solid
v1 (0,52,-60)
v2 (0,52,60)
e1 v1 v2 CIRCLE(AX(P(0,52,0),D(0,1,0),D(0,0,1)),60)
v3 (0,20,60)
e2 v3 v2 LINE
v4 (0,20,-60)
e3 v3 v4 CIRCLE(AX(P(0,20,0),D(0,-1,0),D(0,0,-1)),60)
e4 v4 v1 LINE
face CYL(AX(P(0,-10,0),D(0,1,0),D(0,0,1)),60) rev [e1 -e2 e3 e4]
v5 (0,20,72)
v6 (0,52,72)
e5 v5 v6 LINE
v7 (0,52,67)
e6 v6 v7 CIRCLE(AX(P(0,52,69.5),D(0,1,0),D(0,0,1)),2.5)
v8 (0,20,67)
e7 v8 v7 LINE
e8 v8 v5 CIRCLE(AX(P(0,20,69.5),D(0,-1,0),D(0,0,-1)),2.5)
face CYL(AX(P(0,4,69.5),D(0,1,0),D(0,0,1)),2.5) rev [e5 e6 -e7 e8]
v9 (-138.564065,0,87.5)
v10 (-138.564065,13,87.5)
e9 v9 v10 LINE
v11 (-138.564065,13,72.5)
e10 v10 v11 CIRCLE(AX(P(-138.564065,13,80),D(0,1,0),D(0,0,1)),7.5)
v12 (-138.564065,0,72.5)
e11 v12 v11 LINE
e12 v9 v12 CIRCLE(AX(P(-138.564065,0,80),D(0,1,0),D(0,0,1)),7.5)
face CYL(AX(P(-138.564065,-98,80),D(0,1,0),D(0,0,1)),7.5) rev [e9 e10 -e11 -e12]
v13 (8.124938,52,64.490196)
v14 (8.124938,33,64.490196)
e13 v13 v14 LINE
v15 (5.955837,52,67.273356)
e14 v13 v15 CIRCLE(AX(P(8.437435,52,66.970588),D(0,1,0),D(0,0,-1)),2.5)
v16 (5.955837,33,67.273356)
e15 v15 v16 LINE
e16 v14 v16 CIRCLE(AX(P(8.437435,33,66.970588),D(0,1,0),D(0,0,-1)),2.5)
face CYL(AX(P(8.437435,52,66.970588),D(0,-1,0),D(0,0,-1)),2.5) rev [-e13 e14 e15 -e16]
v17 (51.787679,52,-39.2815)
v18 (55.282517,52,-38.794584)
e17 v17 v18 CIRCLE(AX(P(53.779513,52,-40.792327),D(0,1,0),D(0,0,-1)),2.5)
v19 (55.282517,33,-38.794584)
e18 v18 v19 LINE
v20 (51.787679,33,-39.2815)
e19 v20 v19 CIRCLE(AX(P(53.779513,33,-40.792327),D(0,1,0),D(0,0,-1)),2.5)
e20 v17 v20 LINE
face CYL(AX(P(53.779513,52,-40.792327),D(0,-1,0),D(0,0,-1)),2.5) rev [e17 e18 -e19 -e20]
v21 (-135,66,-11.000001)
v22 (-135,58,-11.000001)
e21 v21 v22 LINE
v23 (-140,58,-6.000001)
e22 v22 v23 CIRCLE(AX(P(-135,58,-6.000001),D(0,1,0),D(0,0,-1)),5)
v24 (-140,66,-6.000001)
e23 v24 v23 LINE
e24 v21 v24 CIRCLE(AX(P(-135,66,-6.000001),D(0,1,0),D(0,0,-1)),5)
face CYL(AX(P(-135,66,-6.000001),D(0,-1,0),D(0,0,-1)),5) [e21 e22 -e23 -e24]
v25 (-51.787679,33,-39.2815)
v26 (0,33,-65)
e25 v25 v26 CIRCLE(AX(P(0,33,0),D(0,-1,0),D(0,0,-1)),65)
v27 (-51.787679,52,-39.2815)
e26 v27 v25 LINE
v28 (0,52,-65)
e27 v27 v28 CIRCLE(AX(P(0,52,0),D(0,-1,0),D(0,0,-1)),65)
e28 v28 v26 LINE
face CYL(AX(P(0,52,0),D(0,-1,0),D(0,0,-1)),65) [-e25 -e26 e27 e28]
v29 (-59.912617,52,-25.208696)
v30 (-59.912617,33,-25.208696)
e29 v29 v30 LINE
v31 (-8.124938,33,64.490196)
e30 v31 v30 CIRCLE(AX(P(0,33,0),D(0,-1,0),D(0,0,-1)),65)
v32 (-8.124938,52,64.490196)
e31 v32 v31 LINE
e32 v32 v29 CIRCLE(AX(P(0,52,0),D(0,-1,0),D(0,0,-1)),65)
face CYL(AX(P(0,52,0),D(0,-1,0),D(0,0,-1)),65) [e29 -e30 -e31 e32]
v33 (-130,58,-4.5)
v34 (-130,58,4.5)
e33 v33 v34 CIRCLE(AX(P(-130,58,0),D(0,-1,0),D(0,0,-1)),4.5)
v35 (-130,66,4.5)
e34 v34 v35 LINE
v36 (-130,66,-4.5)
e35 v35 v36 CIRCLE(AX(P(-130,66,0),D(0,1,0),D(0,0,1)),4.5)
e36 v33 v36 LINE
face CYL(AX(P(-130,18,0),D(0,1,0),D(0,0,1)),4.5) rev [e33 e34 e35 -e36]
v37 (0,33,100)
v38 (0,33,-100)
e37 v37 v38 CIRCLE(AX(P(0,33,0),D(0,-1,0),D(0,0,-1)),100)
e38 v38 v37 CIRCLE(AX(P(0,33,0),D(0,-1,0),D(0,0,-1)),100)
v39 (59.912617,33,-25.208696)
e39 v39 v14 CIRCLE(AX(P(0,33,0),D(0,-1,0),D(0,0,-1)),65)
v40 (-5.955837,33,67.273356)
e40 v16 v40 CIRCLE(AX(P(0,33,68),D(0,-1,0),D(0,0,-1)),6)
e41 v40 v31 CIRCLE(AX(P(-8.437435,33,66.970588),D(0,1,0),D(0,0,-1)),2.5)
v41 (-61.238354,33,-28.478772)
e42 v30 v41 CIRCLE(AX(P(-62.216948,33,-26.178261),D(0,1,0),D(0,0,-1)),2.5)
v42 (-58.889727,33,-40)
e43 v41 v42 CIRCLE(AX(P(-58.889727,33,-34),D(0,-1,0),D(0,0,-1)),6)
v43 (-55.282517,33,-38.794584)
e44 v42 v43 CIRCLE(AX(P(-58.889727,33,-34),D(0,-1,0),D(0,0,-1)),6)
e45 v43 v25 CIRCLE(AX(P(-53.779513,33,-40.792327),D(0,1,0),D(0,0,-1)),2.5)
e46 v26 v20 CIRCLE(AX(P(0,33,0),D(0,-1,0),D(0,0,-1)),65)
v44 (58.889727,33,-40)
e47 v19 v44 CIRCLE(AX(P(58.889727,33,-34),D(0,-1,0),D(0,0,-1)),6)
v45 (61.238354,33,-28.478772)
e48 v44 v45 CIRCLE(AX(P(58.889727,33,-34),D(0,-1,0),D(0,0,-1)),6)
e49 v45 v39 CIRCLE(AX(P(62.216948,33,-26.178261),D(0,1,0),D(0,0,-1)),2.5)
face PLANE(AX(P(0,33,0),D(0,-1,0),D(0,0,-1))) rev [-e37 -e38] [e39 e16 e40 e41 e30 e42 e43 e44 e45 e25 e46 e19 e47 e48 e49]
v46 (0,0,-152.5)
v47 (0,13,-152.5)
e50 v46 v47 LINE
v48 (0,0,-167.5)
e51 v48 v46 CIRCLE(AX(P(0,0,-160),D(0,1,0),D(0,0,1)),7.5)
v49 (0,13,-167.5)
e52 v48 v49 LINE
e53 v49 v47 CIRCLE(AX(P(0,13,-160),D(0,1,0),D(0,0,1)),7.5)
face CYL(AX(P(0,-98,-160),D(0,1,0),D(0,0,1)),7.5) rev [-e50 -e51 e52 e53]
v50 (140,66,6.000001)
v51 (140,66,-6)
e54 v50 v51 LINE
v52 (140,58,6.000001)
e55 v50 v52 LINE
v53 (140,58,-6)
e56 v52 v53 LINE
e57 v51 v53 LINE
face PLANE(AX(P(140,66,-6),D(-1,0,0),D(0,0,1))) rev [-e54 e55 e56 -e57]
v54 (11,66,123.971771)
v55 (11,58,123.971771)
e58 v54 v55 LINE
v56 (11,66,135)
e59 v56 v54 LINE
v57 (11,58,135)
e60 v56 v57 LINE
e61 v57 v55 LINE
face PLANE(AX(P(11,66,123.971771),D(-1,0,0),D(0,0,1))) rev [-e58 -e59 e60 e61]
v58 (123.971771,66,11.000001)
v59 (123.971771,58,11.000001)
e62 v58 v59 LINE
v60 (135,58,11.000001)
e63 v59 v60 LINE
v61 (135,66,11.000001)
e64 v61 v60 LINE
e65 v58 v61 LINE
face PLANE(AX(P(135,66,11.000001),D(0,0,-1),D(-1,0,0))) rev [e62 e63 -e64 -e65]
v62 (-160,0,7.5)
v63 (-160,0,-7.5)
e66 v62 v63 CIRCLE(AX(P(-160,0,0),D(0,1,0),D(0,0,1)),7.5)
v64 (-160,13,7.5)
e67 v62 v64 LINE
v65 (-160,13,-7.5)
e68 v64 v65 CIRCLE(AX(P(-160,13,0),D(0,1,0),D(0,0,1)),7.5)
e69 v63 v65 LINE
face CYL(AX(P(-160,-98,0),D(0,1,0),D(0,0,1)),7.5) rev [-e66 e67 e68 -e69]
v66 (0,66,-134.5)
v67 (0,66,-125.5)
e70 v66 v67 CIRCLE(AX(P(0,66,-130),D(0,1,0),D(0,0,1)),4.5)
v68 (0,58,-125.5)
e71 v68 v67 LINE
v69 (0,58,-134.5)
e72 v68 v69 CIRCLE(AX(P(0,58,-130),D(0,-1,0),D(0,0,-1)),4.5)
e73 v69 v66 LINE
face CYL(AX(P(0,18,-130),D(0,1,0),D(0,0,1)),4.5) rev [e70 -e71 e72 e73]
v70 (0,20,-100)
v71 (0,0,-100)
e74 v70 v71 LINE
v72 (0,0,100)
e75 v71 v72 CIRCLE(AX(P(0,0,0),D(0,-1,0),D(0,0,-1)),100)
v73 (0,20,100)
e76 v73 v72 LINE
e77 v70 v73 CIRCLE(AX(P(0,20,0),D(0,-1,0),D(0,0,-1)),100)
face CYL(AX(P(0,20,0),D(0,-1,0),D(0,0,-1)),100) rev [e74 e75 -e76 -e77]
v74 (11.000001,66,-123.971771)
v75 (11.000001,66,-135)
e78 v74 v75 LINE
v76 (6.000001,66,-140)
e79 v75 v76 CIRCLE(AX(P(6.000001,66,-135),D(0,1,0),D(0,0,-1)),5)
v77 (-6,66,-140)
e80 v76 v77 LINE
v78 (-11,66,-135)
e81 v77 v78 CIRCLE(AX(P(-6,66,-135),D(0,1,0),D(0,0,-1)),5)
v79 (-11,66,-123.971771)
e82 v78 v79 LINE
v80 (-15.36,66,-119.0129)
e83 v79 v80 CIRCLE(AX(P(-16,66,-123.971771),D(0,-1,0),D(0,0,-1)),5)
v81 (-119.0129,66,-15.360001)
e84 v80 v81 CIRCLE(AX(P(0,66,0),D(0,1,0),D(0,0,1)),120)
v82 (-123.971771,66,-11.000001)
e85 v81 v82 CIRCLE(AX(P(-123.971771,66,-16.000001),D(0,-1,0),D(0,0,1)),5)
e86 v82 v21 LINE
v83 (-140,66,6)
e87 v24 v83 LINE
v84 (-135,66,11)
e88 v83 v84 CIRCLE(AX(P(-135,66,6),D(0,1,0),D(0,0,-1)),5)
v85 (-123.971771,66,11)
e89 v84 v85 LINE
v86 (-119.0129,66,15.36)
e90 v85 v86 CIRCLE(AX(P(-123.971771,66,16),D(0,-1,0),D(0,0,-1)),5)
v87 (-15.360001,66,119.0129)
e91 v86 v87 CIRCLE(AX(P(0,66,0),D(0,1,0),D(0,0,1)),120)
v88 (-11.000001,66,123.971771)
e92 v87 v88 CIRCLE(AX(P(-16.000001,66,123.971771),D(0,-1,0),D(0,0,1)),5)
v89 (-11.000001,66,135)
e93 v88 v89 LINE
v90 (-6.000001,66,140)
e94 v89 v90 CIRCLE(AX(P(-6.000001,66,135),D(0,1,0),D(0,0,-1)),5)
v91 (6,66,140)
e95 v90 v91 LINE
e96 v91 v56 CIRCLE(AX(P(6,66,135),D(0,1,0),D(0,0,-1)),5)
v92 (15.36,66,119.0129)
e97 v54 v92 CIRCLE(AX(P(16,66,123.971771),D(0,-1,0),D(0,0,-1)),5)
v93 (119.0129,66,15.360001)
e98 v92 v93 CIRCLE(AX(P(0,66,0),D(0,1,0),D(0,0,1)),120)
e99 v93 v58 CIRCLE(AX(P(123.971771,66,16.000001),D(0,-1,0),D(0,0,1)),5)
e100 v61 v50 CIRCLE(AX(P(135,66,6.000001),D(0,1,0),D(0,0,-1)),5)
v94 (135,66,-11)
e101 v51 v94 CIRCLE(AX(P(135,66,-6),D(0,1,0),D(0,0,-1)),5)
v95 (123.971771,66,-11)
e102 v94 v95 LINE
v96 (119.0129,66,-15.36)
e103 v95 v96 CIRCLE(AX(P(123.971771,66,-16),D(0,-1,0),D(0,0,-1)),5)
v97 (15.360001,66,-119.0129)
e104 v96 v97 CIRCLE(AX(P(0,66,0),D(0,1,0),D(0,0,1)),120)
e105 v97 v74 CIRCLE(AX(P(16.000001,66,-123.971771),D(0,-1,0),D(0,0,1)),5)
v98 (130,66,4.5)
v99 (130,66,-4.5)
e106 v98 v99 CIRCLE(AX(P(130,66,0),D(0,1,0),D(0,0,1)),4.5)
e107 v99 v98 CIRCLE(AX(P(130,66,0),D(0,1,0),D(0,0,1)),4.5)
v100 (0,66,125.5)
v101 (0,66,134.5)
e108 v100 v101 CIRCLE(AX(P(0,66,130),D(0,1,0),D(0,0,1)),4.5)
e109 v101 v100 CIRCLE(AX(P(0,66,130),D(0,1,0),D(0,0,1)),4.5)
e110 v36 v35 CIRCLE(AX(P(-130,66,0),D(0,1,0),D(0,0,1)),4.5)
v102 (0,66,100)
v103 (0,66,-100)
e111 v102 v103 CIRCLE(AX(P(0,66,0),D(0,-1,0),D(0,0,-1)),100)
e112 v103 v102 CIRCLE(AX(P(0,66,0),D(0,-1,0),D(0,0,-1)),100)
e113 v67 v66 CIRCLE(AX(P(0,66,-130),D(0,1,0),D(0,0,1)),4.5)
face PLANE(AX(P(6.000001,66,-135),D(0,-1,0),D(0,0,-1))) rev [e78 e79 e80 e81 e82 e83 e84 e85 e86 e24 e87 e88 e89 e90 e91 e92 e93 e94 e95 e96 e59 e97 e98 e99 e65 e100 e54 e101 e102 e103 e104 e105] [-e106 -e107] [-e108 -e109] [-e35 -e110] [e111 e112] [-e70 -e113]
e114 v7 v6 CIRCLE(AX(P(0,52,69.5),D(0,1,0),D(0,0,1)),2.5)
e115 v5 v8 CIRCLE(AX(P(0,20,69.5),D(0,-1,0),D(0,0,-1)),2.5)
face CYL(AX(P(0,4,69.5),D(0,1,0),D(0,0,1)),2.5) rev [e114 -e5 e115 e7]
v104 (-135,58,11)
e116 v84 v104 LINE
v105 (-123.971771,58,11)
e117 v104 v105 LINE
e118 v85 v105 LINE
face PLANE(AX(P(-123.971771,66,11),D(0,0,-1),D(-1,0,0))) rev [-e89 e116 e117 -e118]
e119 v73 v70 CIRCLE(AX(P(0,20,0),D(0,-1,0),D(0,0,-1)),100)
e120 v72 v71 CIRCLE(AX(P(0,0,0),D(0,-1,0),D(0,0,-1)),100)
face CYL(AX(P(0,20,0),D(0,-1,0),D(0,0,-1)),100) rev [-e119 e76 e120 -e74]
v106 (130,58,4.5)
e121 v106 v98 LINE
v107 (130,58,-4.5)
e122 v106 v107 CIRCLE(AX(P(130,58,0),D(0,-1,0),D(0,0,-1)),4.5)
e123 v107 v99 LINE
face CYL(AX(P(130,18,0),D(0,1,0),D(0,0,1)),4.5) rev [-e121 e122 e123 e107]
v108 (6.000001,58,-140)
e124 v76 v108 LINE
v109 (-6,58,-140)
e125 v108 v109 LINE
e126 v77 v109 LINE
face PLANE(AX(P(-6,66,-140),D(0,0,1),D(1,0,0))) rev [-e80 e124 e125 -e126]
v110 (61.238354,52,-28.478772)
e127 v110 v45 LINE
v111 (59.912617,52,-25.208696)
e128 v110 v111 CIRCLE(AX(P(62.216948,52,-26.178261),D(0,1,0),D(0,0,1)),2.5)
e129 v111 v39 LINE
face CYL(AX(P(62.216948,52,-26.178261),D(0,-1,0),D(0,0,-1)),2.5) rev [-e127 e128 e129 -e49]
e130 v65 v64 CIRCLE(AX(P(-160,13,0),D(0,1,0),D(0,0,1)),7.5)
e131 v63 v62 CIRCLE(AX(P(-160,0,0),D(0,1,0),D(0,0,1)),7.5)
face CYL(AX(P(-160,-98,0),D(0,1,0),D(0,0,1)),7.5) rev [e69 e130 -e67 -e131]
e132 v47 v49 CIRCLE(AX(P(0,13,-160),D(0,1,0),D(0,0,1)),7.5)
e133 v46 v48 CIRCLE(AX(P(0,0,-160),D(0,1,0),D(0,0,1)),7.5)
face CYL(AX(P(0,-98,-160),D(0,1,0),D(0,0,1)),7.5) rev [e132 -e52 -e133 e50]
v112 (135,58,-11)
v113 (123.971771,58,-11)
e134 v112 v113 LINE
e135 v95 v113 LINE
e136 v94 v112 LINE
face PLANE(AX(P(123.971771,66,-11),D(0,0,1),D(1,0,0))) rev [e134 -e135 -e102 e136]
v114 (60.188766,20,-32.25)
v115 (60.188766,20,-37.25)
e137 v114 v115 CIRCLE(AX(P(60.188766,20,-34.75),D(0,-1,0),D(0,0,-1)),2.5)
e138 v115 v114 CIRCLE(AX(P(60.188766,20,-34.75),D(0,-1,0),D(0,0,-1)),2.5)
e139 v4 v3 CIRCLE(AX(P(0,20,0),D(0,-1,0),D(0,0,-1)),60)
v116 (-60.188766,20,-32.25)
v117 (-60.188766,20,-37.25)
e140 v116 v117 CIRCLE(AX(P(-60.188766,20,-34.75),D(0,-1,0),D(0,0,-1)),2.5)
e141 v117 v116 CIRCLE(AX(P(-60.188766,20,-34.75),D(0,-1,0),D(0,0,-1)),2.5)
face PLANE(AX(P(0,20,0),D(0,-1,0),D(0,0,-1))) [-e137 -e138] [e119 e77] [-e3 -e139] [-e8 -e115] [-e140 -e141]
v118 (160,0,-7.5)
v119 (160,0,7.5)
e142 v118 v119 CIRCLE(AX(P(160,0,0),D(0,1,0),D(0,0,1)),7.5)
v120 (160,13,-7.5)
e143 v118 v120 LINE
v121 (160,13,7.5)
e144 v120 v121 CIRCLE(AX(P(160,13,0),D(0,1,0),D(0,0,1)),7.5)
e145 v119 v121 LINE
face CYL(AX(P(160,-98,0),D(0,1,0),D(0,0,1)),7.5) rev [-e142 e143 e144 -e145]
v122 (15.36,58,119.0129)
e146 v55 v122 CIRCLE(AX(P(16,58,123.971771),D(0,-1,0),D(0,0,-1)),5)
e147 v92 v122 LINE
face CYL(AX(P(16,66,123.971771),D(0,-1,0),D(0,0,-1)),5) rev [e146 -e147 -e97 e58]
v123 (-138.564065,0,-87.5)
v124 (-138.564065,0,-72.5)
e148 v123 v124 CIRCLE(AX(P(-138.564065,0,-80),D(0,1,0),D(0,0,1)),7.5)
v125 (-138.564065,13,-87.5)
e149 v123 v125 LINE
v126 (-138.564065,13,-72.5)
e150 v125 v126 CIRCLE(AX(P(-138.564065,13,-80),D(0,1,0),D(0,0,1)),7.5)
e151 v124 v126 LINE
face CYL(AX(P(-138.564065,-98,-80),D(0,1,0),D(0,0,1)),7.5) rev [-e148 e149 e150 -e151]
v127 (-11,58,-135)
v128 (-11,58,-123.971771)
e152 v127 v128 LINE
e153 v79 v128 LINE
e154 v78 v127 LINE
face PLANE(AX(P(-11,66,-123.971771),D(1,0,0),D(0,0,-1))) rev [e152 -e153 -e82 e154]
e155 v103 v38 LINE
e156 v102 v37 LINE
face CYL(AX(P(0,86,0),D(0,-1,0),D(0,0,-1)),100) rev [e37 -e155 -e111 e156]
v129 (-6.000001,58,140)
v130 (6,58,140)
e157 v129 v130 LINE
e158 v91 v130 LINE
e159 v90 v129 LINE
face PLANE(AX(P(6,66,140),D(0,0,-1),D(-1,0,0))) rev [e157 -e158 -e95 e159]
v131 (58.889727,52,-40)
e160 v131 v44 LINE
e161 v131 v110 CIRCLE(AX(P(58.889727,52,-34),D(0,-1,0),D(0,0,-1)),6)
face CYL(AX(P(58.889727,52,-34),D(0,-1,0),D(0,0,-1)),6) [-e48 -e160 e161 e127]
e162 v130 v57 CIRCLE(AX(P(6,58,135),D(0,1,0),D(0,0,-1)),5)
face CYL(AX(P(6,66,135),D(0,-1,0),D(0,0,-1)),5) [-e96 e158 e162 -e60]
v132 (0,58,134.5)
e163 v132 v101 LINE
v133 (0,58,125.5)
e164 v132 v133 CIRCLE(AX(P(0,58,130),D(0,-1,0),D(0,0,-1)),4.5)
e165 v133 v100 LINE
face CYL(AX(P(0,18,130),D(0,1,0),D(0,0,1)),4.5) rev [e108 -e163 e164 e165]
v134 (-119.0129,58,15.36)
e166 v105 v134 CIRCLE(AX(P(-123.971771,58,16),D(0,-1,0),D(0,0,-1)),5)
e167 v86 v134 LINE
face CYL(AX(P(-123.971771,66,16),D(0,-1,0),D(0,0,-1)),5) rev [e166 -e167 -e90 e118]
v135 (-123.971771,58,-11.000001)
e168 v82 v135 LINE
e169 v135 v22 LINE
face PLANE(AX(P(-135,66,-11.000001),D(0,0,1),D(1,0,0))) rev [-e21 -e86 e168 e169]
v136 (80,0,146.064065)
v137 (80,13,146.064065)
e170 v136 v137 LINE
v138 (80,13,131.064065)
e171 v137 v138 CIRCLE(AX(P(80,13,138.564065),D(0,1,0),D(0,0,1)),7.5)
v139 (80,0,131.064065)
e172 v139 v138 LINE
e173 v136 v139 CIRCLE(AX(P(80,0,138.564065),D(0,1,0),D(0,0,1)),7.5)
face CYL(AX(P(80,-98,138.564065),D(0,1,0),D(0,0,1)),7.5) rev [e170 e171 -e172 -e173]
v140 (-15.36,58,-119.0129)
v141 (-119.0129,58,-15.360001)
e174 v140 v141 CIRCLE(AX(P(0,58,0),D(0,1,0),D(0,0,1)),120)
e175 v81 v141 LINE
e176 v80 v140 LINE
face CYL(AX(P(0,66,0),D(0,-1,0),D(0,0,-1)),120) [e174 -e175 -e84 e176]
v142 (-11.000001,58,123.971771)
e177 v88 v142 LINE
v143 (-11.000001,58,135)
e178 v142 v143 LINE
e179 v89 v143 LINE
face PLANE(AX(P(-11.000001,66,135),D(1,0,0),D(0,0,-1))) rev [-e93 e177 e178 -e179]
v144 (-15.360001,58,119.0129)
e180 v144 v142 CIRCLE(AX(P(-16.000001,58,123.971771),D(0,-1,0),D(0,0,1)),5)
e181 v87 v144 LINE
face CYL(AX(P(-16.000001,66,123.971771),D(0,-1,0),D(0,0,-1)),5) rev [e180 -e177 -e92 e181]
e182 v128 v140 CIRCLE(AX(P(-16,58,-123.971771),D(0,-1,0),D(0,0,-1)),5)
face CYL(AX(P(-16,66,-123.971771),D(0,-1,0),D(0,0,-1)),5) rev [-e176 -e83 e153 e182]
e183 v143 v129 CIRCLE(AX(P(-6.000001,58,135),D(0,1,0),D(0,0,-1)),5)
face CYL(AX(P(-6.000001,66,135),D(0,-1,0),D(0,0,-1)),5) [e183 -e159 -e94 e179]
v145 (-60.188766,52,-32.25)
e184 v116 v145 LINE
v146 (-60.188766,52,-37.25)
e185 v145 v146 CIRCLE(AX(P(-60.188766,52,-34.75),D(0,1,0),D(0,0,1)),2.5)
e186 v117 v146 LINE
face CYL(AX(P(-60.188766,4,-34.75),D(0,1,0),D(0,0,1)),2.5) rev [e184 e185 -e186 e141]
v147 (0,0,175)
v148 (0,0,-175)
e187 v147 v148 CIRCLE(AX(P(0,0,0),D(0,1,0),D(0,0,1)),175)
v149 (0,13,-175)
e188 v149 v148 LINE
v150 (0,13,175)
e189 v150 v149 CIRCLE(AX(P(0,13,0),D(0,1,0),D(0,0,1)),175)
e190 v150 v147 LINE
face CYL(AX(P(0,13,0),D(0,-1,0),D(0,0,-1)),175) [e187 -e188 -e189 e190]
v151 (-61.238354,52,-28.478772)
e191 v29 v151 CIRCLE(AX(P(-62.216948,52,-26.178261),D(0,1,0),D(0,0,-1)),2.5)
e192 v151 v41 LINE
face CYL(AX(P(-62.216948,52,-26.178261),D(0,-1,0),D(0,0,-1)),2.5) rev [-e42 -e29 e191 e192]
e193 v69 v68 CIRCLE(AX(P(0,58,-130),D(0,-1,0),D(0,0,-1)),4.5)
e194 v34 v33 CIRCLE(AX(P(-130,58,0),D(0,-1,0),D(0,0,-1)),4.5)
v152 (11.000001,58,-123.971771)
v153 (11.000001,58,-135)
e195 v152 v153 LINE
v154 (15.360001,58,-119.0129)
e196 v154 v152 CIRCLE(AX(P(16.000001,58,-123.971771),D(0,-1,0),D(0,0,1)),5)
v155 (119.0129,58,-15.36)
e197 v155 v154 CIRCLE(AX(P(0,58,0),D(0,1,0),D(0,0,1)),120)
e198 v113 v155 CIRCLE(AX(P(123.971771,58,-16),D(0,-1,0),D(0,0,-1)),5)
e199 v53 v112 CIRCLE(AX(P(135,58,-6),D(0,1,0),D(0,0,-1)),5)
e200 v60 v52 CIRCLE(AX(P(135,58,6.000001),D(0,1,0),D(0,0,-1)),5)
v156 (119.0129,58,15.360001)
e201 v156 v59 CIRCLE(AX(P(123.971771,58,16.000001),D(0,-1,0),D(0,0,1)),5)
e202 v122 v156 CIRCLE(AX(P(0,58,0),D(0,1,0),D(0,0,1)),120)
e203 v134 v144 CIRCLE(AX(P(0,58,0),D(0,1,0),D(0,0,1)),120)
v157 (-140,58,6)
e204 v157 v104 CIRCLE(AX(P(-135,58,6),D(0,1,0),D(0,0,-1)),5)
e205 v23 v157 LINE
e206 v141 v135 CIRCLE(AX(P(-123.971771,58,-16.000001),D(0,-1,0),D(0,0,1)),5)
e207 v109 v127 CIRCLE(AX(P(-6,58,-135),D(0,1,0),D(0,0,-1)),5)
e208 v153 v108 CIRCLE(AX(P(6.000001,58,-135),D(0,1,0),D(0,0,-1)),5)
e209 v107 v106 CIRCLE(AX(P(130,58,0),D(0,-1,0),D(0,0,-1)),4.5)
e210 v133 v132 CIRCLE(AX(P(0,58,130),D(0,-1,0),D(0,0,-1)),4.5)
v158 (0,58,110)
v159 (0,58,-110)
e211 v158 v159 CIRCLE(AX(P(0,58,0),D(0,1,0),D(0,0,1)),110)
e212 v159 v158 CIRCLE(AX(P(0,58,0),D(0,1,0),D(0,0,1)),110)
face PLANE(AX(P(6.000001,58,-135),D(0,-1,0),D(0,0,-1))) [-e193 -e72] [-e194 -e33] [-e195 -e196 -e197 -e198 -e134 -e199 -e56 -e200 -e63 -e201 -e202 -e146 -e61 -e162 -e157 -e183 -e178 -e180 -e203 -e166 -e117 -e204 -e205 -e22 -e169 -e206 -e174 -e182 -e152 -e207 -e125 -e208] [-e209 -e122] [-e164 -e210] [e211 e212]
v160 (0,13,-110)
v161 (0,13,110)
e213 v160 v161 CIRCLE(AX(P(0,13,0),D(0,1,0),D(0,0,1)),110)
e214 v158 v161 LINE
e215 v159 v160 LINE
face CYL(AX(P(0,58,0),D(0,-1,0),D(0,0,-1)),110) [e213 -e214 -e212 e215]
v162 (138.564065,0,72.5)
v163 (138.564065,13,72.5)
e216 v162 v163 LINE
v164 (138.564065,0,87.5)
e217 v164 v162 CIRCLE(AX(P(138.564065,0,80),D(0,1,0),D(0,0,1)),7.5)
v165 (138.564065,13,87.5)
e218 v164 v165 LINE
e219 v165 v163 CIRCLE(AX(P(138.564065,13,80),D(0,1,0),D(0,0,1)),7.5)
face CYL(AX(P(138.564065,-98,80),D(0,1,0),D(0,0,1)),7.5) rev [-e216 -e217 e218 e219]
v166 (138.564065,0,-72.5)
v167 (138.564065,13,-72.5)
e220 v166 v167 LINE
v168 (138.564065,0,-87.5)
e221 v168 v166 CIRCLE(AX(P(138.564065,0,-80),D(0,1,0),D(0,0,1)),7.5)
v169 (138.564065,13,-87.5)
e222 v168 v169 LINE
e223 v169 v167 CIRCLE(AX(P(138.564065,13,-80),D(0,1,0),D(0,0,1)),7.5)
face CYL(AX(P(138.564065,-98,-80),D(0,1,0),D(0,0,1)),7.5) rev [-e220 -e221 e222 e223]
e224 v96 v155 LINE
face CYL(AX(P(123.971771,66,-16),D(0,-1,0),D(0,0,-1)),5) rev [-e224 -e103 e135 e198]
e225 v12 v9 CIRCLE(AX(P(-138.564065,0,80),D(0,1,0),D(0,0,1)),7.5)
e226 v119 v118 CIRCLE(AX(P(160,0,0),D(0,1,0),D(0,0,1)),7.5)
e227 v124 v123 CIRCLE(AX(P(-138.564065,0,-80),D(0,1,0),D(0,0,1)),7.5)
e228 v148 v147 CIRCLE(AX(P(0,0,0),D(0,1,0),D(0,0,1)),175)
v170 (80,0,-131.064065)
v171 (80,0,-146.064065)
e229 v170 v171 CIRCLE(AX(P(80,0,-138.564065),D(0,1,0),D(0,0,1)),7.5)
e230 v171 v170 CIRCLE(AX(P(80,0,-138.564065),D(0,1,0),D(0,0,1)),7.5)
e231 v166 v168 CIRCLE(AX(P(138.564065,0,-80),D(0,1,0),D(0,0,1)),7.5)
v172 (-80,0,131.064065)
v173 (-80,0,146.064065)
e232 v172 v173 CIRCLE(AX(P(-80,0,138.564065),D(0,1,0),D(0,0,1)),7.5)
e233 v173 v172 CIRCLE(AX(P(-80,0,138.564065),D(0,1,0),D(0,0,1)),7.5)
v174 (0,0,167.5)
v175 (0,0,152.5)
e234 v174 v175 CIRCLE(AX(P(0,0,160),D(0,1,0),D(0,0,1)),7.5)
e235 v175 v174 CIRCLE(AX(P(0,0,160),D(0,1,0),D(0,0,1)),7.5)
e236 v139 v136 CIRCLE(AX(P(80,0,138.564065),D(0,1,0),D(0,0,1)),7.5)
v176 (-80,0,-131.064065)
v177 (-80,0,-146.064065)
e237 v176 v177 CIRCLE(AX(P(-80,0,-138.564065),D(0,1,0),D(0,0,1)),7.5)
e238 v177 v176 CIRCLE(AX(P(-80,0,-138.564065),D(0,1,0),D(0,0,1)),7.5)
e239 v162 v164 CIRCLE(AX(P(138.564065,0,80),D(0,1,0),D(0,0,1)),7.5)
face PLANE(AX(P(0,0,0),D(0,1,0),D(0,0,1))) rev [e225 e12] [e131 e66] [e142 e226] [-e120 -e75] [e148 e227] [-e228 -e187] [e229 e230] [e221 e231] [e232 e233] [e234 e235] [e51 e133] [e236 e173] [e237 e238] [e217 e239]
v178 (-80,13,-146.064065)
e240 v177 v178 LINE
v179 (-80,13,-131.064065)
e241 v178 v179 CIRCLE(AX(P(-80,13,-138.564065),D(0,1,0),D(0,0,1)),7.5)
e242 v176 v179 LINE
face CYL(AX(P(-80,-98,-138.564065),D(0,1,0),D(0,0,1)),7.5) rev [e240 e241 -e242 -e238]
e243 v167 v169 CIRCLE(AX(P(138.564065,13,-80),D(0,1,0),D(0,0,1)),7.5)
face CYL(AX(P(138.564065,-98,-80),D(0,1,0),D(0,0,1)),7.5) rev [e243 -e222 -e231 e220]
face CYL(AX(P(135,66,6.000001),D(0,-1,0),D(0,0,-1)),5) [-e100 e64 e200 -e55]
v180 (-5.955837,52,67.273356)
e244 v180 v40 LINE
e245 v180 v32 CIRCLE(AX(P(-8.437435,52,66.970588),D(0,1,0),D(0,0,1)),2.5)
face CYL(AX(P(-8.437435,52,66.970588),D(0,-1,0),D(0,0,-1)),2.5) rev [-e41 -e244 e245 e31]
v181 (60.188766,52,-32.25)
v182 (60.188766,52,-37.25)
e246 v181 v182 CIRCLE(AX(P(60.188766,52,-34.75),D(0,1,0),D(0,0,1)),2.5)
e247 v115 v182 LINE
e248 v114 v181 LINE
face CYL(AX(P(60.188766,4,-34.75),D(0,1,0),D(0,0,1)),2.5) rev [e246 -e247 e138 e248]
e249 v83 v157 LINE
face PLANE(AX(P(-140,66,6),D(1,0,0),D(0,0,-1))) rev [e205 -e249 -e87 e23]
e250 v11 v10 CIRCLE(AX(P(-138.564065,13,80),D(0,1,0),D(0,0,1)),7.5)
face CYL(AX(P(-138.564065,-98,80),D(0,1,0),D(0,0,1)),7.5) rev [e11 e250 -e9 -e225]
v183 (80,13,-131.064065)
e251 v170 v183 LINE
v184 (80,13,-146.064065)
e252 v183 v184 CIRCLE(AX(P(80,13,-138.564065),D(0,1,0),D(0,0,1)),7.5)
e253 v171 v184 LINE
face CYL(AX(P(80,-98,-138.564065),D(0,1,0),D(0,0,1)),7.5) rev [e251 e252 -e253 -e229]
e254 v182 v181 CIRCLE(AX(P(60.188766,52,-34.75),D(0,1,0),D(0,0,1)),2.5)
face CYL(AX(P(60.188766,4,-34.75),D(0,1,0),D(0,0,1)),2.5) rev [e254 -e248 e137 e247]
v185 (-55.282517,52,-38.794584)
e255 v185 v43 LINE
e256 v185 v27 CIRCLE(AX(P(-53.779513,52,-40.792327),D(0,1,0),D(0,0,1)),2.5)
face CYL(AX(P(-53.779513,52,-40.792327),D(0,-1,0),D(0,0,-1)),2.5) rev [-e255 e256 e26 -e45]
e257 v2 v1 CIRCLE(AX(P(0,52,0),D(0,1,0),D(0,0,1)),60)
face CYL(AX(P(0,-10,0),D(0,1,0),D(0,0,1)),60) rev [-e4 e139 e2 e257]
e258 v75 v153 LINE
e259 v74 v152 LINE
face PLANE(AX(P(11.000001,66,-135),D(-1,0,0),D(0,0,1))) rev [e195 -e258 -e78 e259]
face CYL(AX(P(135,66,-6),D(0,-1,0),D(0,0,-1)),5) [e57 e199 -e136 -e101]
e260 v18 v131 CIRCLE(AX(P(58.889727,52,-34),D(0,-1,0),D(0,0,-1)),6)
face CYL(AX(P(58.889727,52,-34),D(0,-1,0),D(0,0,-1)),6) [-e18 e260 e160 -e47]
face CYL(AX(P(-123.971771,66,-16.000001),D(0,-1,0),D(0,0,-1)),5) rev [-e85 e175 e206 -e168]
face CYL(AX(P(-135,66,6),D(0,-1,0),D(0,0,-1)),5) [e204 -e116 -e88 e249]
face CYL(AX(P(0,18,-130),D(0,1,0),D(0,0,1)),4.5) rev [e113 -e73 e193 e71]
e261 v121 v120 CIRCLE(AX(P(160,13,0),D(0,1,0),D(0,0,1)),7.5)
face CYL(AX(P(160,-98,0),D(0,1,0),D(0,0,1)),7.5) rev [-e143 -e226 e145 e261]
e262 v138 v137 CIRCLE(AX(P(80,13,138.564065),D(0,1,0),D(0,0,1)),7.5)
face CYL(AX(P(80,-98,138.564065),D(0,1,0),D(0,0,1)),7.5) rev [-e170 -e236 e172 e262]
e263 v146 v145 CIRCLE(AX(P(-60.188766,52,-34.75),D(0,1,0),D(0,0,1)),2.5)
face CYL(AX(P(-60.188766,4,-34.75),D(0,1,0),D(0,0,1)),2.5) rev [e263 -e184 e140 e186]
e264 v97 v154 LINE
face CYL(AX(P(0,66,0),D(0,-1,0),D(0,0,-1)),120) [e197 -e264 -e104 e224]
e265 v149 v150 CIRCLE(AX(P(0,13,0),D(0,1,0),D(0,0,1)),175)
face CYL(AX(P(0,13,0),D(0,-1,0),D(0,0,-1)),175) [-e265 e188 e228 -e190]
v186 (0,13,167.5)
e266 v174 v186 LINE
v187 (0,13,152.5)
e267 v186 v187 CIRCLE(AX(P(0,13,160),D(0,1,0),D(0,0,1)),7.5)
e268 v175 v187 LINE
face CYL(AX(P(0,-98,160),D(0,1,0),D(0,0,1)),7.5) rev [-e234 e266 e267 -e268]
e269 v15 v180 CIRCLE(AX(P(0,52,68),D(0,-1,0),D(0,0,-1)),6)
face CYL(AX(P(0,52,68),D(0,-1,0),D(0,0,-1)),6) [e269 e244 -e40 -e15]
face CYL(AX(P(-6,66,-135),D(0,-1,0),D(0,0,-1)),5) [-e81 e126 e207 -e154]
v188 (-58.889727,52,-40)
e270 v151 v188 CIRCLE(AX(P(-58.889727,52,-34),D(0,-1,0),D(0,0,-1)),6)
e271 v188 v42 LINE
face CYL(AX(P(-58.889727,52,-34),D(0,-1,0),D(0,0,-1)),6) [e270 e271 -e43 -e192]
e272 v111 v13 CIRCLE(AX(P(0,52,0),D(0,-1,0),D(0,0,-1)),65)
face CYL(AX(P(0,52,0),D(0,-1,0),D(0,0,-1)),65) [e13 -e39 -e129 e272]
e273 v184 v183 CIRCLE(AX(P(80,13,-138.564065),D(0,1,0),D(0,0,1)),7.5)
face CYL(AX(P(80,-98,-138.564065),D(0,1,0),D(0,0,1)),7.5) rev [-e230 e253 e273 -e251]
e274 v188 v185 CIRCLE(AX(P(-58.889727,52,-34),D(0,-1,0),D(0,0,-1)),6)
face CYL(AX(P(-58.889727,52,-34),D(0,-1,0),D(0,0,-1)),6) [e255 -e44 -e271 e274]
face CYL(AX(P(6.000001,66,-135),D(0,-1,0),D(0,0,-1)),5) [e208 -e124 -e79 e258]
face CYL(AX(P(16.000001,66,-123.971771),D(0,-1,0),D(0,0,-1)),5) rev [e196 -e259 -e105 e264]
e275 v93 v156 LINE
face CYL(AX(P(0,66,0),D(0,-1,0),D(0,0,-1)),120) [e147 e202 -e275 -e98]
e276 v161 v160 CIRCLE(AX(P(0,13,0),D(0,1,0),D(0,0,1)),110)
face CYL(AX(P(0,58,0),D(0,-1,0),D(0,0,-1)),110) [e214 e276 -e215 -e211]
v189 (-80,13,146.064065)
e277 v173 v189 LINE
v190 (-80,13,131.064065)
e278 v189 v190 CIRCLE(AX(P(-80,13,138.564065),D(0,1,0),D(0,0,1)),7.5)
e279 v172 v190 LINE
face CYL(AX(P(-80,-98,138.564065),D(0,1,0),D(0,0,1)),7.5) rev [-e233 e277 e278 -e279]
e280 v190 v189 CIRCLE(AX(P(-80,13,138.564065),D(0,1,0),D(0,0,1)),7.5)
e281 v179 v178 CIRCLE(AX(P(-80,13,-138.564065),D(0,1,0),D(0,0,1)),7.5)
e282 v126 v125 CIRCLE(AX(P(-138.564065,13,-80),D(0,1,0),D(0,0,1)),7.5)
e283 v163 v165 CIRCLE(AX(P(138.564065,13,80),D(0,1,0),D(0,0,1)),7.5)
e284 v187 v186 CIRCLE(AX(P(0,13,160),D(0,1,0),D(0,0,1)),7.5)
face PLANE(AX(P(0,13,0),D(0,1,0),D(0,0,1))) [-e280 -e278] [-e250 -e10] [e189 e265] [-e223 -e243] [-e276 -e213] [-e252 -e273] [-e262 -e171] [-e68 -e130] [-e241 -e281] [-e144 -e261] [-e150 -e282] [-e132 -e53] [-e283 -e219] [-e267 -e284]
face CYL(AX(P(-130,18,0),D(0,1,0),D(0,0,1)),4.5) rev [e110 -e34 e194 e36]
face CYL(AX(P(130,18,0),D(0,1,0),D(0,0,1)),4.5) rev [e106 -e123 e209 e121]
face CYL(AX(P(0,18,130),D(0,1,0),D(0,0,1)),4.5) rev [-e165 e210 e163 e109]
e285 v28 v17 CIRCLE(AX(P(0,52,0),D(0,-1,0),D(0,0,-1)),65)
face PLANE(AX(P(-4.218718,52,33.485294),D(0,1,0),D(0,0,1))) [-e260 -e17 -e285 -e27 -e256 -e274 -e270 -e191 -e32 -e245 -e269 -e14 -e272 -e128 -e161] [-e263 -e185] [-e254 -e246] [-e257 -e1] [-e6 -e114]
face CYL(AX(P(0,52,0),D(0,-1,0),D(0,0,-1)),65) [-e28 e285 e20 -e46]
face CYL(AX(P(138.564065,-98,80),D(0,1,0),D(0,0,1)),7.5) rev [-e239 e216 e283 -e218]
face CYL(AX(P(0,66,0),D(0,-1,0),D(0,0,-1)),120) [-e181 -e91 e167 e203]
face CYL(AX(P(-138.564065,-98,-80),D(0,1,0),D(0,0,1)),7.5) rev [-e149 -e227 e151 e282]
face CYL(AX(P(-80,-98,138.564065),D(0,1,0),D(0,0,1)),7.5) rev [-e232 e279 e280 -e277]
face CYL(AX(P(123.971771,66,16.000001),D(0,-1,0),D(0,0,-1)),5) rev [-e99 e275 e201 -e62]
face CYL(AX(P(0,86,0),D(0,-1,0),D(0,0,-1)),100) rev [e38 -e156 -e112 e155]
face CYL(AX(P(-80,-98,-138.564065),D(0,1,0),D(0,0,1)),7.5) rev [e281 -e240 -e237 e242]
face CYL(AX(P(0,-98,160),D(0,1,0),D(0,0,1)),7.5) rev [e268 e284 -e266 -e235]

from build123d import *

# Parameters (mm, degrees)
BASE_FLANGE_SKETCH_R      = 175
BASE_FLANGE_350_DEPTH     = 13
HUB_SKETCH_R              = 110
HUB_BOSS_220_DEPTH        = 45
MOUNTING_LUGS_4X_DEPTH    = 8
BOLT_HOLES_SKETCH_R       = 7.5
BOLT_HOLES_12X_15_DEPTH   = 111
UPPER_BORE_SKETCH_R       = 100
UPPER_BORE_200_DEPTH      = 20
INNER_RECESS_SKETCH_R     = 33
INNER_RECESS_CUT_DEPTH    = 13
LOWER_BORE_SKETCH_R       = 100
LOWER_BORE_200_DEPTH      = 53
INNER_RING_BOSS_DEPTH     = 32
CENTRE_BORE_SKETCH_R      = 60
CENTRE_BORE_120_DEPTH     = 62
LUG_NOTCH_SKETCH_R        = 4.5
LUG_NOTCH_CUT_DEPTH       = 48
INNER_RING_SLOTS_SKETCH_R = 2.5
INNER_RING_SLOTS_3X_DEPTH = 48


with BuildPart() as part:
    # Base Flange Sketch → Base Flange Ø350 (new body)
    with BuildSketch(Plane(origin=(0, 0, 0), x_dir=(1, 0, 0), z_dir=(0, 1, 0))):
        with Locations(Location((0, 0, 0), (0, 0, 90))):
            Circle(BASE_FLANGE_SKETCH_R)
    extrude(amount=BASE_FLANGE_350_DEPTH)

    # Hub Sketch → Hub Boss Ø220 (add)
    with BuildSketch(Plane(origin=(0, 13, 0), x_dir=(1, 0, 0), z_dir=(0, 1, 0))):
        with Locations(Location((0, 0, 0), (0, 0, 90))):
            Circle(HUB_SKETCH_R)
    extrude(amount=HUB_BOSS_220_DEPTH)

    # Mounting Lugs Sketch → Mounting Lugs 4x (add)
    with BuildSketch(Plane(origin=(0, 58, 0), x_dir=(1, 0, 0), z_dir=(0, 1, 0))):
        with BuildLine():
            Line((123.97177098, 11), (135, 11))
            ThreePointArc((135, 11), (138.535533906, 9.535533906), (140, 6))
            Line((140, 6), (140, 0))
            Line((140, 0), (140, -6.000000959))
            ThreePointArc((140, -6.000000959), (138.535533906, -9.535534865), (135, -11.000000959))
            Line((135, -11.000000959), (123.971770857, -11.000000959))
            ThreePointArc((123.971770857, -11.000000959), (120.670256067, -12.245004275), (119.012900022, -15.360000921))
            ThreePointArc((119.012900022, -15.360000921), (84.852813414, -84.852814071), (15.36, -119.012900141))
            ThreePointArc((15.36, -119.012900141), (12.245003329, -120.670256176), (11, -123.97177098))
            Line((11, -123.97177098), (11, -135))
            ThreePointArc((11, -135), (9.535533906, -138.535533906), (6, -140))
            Line((6, -140), (0, -140))
            Line((0, -140), (-6.000000959, -140))
            ThreePointArc((-6.000000959, -140), (-9.535534865, -138.535533906), (-11.000000959, -135))
            Line((-11.000000959, -135), (-11.000000959, -123.971770857))
            ThreePointArc((-11.000000959, -123.971770857), (-12.245004275, -120.670256067), (-15.360000921, -119.012900022))
            ThreePointArc((-15.360000921, -119.012900022), (-84.852814071, -84.852813414), (-119.012900141, -15.36))
            ThreePointArc((-119.012900141, -15.36), (-120.670256176, -12.245003329), (-123.97177098, -11))
            Line((-123.97177098, -11), (-135, -11))
            ThreePointArc((-135, -11), (-138.535533906, -9.535533906), (-140, -6))
            Line((-140, -6), (-140, 0))
            Line((-140, 0), (-140, 6.000000959))
            ThreePointArc((-140, 6.000000959), (-138.535533906, 9.535534865), (-135, 11.000000959))
            Line((-135, 11.000000959), (-123.971770857, 11.000000959))
            ThreePointArc((-123.971770857, 11.000000959), (-120.670256067, 12.245004275), (-119.012900022, 15.360000921))
            ThreePointArc((-119.012900022, 15.360000921), (-84.852813414, 84.852814071), (-15.36, 119.012900141))
            ThreePointArc((-15.36, 119.012900141), (-12.245003329, 120.670256176), (-11, 123.97177098))
            Line((-11, 123.97177098), (-11, 135))
            ThreePointArc((-11, 135), (-9.535533906, 138.535533906), (-6, 140))
            Line((-6, 140), (0, 140))
            Line((0, 140), (6.000000959, 140))
            ThreePointArc((6.000000959, 140), (9.535534865, 138.535533906), (11.000000959, 135))
            Line((11.000000959, 135), (11.000000959, 123.971770857))
            ThreePointArc((11.000000959, 123.971770857), (12.245004275, 120.670256067), (15.360000921, 119.012900022))
            ThreePointArc((15.360000921, 119.012900022), (84.852814071, 84.852813414), (119.012900141, 15.36))
            ThreePointArc((119.012900141, 15.36), (120.670256176, 12.245003329), (123.97177098, 11))
        make_face()
    extrude(amount=MOUNTING_LUGS_4X_DEPTH)

    # Bolt Holes Sketch → Bolt Holes 12xØ15 (cut)
    with BuildSketch(Plane(origin=(0, 13, 0), x_dir=(1, 0, 0), z_dir=(0, 1, 0))):
        with Locations(Location((0, 160, 0), (0, 0, 270))):
            Circle(BOLT_HOLES_SKETCH_R)
        with Locations(Location((80, 138.564064606, 0), (0, 0, 270))):
            Circle(BOLT_HOLES_SKETCH_R)
        with Locations(Location((138.564064606, 80, 0), (0, 0, 270))):
            Circle(BOLT_HOLES_SKETCH_R)
        with Locations(Location((160, 0, 0), (0, 0, 270))):
            Circle(BOLT_HOLES_SKETCH_R)
        with Locations(Location((138.564064606, -80, 0), (0, 0, 270))):
            Circle(BOLT_HOLES_SKETCH_R)
        with Locations(Location((80, -138.564064605, 0), (0, 0, 270))):
            Circle(BOLT_HOLES_SKETCH_R)
        with Locations(Location((0, -160, 0), (0, 0, 270))):
            Circle(BOLT_HOLES_SKETCH_R)
        with Locations(Location((-80, -138.564064606, 0), (0, 0, 270))):
            Circle(BOLT_HOLES_SKETCH_R)
        with Locations(Location((-138.564064605, -80, 0), (0, 0, 270))):
            Circle(BOLT_HOLES_SKETCH_R)
        with Locations(Location((-160, 0, 0), (0, 0, 270))):
            Circle(BOLT_HOLES_SKETCH_R)
        with Locations(Location((-138.564064605, 80, 0), (0, 0, 270))):
            Circle(BOLT_HOLES_SKETCH_R)
        with Locations(Location((-80, 138.564064605, 0), (0, 0, 270))):
            Circle(BOLT_HOLES_SKETCH_R)
    extrude(amount=-BOLT_HOLES_12X_15_DEPTH, mode=Mode.SUBTRACT)

    # Upper Bore Sketch → Upper Bore Ø200 (cut)
    with BuildSketch(Plane.XZ):
        with Locations(Location((0, 0, 0), (0, 0, 270))):
            Circle(UPPER_BORE_SKETCH_R)
    extrude(amount=-UPPER_BORE_200_DEPTH, mode=Mode.SUBTRACT)

    # Inner Recess Sketch → Inner Recess Cut (cut)
    with BuildSketch(Plane.XZ.offset(-20)):
        with Locations(Location((0, 0, 0), (0, 0, 270))):
            Circle(INNER_RECESS_SKETCH_R)
    extrude(amount=-INNER_RECESS_CUT_DEPTH, mode=Mode.SUBTRACT)

    # Lower Bore Sketch → Lower Bore Ø200 (cut)
    with BuildSketch(Plane.XZ.offset(-33)):
        with Locations(Location((0, 0, 0), (0, 0, 270))):
            Circle(LOWER_BORE_SKETCH_R)
    extrude(amount=-LOWER_BORE_200_DEPTH, mode=Mode.SUBTRACT)

    # Inner Ring Sketch → Inner Ring Boss (add)
    with BuildSketch(Plane.XZ.offset(-20)):
        with BuildLine():
            ThreePointArc((-8.124937524, 64.490196078), (-56.291651246, 32.5), (-59.912616861, -25.208695739))
            ThreePointArc((-59.912616861, -25.208695739), (-59.900107579, -27.117542161), (-61.238353919, -28.478772442))
            ThreePointArc((-61.238353919, -28.478772442), (-64.08587988, -37), (-55.282517363, -38.794583959))
            ThreePointArc((-55.282517363, -38.794583959), (-53.43453419, -38.316243773), (-51.787679337, -39.281500339))
            ThreePointArc((-51.787679337, -39.281500339), (0, -65), (51.787679337, -39.281500339))
            ThreePointArc((51.787679337, -39.281500339), (53.43453419, -38.316243773), (55.282517363, -38.794583959))
            ThreePointArc((55.282517363, -38.794583959), (64.08587988, -37), (61.238353919, -28.478772442))
            ThreePointArc((61.238353919, -28.478772442), (59.900107579, -27.117542161), (59.912616861, -25.208695739))
            ThreePointArc((59.912616861, -25.208695739), (56.291651246, 32.5), (8.124937524, 64.490196078))
            ThreePointArc((8.124937524, 64.490196078), (6.46557339, 65.433785934), (5.955836556, 67.273356401))
            ThreePointArc((5.955836556, 67.273356401), (0, 74), (-5.955836556, 67.273356401))
            ThreePointArc((-5.955836556, 67.273356401), (-6.46557339, 65.433785934), (-8.124937524, 64.490196078))
        make_face()
    extrude(amount=-INNER_RING_BOSS_DEPTH)

    # Centre Bore Sketch → Centre Bore Ø120 (cut)
    with BuildSketch(Plane(origin=(0, 52, 0), x_dir=(1, 0, 0), z_dir=(0, 1, 0))):
        with Locations(Location((0, 0, 0), (0, 0, 270))):
            Circle(CENTRE_BORE_SKETCH_R)
    extrude(amount=-CENTRE_BORE_120_DEPTH, mode=Mode.SUBTRACT)

    # Lug Notch Sketch → Lug Notch Cut (cut)
    with BuildSketch(Plane(origin=(0, 66, 0), x_dir=(1, 0, 0), z_dir=(0, 1, 0))):
        with Locations(Location((0, 130, 0), (0, 0, 270))):
            Circle(LUG_NOTCH_SKETCH_R)
        with Locations(Location((130, 0, 0), (0, 0, 270))):
            Circle(LUG_NOTCH_SKETCH_R)
        with Locations(Location((0, -130, 0), (0, 0, 270))):
            Circle(LUG_NOTCH_SKETCH_R)
        with Locations(Location((-130, 0, 0), (0, 0, 270))):
            Circle(LUG_NOTCH_SKETCH_R)
    extrude(amount=-LUG_NOTCH_CUT_DEPTH, mode=Mode.SUBTRACT)

    # Inner Ring Slots Sketch → Inner Ring Slots 3x (cut)
    with BuildSketch(Plane(origin=(0, 52, 0), x_dir=(1, 0, 0), z_dir=(0, 1, 0))):
        with Locations(Location((0, -69.5, 0), (0, 0, 270))):
            Circle(INNER_RING_SLOTS_SKETCH_R)
        with Locations(Location((-60.188765563, 34.75, 0), (0, 0, 270))):
            Circle(INNER_RING_SLOTS_SKETCH_R)
        with Locations(Location((60.188765563, 34.75, 0), (0, 0, 270))):
            Circle(INNER_RING_SLOTS_SKETCH_R)
    extrude(amount=-INNER_RING_SLOTS_3X_DEPTH, mode=Mode.SUBTRACT)


solid = part.part
